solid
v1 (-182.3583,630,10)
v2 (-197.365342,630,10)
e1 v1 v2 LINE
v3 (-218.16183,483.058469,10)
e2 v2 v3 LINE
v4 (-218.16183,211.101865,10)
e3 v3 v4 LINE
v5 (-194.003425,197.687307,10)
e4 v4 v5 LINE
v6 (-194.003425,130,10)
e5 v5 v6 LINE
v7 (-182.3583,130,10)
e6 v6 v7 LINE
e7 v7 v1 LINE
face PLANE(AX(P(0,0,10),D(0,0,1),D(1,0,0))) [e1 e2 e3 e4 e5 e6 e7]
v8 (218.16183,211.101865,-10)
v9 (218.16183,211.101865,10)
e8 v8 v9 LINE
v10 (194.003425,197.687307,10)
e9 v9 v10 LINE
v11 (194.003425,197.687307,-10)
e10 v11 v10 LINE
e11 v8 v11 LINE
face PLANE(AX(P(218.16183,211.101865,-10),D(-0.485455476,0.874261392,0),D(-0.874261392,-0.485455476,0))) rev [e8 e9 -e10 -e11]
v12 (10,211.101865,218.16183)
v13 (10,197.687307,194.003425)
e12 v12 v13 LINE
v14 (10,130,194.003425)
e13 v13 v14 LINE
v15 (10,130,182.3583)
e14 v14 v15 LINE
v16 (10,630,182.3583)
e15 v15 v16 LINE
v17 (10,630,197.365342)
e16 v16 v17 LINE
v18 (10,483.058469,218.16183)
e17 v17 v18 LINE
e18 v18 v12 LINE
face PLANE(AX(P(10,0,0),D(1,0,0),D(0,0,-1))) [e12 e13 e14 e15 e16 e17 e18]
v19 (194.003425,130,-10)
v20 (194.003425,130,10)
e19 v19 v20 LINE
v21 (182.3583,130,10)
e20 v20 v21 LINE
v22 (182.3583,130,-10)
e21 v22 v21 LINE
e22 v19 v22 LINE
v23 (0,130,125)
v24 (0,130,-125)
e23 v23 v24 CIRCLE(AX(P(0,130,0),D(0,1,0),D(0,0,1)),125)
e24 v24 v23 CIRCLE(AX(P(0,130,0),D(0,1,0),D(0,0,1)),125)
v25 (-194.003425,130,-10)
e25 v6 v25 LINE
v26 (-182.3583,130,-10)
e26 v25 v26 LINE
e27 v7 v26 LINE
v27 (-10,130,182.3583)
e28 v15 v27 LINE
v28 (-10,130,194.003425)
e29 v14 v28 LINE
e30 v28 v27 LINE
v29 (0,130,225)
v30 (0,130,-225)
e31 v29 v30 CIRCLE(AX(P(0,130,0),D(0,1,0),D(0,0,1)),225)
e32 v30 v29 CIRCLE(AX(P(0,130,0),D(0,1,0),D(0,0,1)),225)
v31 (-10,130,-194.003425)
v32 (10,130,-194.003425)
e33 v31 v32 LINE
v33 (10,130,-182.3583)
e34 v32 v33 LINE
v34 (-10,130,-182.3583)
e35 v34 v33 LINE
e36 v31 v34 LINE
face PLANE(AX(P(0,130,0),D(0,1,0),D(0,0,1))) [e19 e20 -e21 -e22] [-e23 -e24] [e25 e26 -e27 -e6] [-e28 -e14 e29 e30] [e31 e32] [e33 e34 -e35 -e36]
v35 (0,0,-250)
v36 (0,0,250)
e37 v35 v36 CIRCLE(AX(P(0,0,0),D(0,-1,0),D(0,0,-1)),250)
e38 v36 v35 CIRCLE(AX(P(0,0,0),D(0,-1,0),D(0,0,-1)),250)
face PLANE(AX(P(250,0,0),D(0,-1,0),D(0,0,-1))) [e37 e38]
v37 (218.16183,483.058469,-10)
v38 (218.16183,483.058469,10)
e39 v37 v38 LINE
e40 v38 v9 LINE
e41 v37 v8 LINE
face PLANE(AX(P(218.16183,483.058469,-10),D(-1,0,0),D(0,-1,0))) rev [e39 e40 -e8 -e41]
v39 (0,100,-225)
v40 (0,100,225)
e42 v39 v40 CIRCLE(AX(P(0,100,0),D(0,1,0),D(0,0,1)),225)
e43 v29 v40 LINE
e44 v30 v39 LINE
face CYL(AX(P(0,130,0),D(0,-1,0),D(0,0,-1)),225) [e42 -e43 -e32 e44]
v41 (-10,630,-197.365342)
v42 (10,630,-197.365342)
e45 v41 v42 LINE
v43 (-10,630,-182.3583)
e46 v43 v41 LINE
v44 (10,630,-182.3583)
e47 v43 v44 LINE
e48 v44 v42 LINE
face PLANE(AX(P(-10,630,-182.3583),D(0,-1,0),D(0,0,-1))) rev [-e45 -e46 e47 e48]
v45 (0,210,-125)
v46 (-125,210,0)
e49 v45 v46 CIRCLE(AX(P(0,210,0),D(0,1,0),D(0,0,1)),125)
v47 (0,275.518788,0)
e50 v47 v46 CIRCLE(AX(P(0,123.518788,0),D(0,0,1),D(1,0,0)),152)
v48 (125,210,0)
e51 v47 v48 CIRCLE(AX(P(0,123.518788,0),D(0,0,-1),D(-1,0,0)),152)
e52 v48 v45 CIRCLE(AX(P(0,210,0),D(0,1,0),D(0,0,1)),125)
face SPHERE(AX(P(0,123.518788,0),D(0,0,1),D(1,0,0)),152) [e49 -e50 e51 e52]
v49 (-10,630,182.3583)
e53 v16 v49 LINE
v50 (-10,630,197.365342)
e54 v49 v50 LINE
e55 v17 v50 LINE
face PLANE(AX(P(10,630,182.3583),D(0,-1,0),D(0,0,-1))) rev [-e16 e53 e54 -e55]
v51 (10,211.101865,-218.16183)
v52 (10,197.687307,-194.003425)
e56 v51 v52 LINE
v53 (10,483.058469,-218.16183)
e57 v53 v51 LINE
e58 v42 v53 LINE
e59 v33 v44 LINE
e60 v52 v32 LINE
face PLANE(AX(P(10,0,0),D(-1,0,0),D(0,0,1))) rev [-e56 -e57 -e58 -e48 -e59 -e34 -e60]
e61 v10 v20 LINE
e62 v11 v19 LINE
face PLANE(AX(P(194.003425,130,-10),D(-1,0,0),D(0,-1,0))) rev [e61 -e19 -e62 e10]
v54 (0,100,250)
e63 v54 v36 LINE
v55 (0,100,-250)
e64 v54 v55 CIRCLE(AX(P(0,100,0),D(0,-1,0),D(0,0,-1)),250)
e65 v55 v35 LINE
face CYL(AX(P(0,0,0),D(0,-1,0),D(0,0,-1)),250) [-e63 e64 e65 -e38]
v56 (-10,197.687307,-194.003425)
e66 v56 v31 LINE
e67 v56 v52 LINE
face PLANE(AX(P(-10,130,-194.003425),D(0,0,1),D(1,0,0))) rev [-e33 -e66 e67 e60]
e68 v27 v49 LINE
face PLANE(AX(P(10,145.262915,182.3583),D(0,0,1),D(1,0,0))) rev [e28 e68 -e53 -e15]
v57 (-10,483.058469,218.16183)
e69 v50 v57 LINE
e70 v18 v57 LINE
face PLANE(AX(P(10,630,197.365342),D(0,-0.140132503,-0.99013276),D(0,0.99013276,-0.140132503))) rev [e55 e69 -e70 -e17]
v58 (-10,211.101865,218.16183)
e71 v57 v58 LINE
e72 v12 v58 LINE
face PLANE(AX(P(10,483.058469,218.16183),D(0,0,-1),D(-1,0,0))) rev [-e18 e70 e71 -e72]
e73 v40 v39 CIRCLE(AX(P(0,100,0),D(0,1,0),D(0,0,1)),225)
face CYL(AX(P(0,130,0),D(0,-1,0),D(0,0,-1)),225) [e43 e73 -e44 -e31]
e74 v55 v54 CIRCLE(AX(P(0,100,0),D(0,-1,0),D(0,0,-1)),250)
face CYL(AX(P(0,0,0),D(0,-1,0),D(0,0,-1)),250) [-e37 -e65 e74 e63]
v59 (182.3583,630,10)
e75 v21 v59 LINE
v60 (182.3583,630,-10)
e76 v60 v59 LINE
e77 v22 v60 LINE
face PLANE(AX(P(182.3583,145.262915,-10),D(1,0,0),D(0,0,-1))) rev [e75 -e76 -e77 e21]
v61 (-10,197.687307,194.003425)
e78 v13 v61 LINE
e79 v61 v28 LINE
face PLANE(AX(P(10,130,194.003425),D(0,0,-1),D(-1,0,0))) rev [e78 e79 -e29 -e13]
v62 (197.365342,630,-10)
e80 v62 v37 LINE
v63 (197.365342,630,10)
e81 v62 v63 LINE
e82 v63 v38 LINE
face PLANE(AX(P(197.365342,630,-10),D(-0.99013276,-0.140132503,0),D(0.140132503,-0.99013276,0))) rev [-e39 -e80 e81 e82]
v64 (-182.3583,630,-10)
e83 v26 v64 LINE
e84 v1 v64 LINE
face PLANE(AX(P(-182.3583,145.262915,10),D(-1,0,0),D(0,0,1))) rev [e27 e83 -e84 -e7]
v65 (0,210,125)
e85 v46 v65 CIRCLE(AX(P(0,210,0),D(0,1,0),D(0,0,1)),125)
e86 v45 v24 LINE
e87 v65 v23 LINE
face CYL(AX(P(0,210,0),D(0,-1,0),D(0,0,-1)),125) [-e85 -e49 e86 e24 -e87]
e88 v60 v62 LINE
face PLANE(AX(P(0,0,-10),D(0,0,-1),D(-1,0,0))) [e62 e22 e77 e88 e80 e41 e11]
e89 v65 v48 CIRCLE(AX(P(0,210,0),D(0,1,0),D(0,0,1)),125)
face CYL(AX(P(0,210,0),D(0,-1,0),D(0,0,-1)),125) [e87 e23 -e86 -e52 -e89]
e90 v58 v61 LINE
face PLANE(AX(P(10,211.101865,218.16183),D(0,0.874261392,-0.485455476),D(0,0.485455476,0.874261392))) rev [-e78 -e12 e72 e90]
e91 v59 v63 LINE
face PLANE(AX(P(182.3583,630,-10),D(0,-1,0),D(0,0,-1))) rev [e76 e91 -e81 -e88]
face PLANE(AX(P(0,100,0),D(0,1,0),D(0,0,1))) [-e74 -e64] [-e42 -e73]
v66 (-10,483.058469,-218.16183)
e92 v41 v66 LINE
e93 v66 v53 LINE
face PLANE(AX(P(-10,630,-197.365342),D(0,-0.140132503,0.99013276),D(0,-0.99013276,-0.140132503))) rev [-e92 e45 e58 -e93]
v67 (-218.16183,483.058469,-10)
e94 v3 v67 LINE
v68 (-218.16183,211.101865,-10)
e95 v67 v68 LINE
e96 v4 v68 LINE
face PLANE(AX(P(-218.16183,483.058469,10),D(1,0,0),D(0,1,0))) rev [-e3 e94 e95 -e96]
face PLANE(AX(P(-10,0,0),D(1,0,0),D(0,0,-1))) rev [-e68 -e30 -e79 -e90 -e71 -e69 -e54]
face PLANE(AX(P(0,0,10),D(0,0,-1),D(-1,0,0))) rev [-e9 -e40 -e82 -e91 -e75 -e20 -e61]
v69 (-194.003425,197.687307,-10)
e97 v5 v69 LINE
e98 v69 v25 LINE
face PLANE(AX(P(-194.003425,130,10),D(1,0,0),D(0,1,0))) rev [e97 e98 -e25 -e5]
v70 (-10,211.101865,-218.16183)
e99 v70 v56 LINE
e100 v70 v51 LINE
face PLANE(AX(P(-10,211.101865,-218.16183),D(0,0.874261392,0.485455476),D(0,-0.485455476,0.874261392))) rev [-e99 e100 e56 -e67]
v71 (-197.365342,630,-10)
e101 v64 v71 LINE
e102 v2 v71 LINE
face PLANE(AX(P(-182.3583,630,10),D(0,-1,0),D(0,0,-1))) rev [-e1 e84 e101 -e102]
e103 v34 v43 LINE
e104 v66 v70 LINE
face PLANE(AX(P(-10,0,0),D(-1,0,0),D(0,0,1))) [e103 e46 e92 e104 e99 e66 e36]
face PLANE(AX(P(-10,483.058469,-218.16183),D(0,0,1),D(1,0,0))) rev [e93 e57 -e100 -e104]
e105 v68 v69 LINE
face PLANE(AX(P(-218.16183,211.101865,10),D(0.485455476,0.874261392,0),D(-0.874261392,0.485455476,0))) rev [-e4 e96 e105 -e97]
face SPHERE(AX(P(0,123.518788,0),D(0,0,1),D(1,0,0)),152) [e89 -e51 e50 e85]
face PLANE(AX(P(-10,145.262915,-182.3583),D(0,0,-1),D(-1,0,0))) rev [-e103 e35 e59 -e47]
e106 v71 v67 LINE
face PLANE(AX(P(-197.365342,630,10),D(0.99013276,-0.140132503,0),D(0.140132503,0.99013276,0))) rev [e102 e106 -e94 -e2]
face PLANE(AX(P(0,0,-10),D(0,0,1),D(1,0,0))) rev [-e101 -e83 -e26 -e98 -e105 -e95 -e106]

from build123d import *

# Parameters (mm, degrees)
SKETCH1_W           = 250
SKETCH1_H           = 100
SKETCH2_R           = 225
BOSS_EXTRUDE1_DEPTH = 30
SKETCH3_R           = 125
BOSS_EXTRUDE2_DEPTH = 80
BOSS_EXTRUDE3_DEPTH = 10
CIRPATTERN1_COUNT   = 4


with BuildPart() as part:
    # Sketch1 → Revolve1 (revolve)
    with BuildSketch(Plane.XY, mode=Mode.PRIVATE) as revolve1_sk:
        with Locations((125, 50)):
            Rectangle(SKETCH1_W, SKETCH1_H)
    revolve(revolve1_sk.sketch.rotate(Axis((0, 0, 0), (0, 1, 0)), 90), axis=Axis((0, 0, 0), (0, 1, 0)))

    # Sketch2 → Boss-Extrude1 (add)
    with BuildSketch(Plane(origin=(0, 100, 0), x_dir=(1, 0, 0), z_dir=(0, 1, 0))):
        with Locations(Location((0, 0, 0), (0, 0, 270))):
            Circle(SKETCH2_R)
    extrude(amount=BOSS_EXTRUDE1_DEPTH)

    # Sketch3 → Boss-Extrude2 (add)
    with BuildSketch(Plane(origin=(0, 130, 0), x_dir=(1, 0, 0), z_dir=(0, 1, 0))):
        with Locations(Location((0, 0, 0), (0, 0, 270))):
            Circle(SKETCH3_R)
    extrude(amount=BOSS_EXTRUDE2_DEPTH)

    # Sketch4 → Revolve2 (revolve)
    with BuildSketch(Plane.XY):
        with BuildLine():
            Line((0, 210), (0, 275.518788168))
            ThreePointArc((0, 275.518788168), (70.565061473, 258.146319153), (125, 210))
            Line((125, 210), (0, 210))
        make_face()
    revolve(axis=Axis((0, 210, 0), (0, 1, 0)))

    # Sketch5 → Boss-Extrude3 (add, symmetric)
    with BuildSketch(Plane.XY):
        Polygon((-194.003425054, 130), (-182.358299763, 130), (-182.358299763, 145.262915146), (-182.358299763, 630), (-197.365341888, 630), (-218.16183032, 483.058469024), (-218.16183032, 211.101864805), (-194.003425054, 197.687306821), align=None)
    boss_extrude3 = extrude(amount=BOSS_EXTRUDE3_DEPTH, both=True)

    # CirPattern1: Boss-Extrude3 ×4 about axis
    cirpattern1_axis = Axis((0, 0, 0), (0, 1, 0))
    for i in range(1, CIRPATTERN1_COUNT):
        add(boss_extrude3.rotate(cirpattern1_axis, i * 360 / CIRPATTERN1_COUNT))


solid = part.part
